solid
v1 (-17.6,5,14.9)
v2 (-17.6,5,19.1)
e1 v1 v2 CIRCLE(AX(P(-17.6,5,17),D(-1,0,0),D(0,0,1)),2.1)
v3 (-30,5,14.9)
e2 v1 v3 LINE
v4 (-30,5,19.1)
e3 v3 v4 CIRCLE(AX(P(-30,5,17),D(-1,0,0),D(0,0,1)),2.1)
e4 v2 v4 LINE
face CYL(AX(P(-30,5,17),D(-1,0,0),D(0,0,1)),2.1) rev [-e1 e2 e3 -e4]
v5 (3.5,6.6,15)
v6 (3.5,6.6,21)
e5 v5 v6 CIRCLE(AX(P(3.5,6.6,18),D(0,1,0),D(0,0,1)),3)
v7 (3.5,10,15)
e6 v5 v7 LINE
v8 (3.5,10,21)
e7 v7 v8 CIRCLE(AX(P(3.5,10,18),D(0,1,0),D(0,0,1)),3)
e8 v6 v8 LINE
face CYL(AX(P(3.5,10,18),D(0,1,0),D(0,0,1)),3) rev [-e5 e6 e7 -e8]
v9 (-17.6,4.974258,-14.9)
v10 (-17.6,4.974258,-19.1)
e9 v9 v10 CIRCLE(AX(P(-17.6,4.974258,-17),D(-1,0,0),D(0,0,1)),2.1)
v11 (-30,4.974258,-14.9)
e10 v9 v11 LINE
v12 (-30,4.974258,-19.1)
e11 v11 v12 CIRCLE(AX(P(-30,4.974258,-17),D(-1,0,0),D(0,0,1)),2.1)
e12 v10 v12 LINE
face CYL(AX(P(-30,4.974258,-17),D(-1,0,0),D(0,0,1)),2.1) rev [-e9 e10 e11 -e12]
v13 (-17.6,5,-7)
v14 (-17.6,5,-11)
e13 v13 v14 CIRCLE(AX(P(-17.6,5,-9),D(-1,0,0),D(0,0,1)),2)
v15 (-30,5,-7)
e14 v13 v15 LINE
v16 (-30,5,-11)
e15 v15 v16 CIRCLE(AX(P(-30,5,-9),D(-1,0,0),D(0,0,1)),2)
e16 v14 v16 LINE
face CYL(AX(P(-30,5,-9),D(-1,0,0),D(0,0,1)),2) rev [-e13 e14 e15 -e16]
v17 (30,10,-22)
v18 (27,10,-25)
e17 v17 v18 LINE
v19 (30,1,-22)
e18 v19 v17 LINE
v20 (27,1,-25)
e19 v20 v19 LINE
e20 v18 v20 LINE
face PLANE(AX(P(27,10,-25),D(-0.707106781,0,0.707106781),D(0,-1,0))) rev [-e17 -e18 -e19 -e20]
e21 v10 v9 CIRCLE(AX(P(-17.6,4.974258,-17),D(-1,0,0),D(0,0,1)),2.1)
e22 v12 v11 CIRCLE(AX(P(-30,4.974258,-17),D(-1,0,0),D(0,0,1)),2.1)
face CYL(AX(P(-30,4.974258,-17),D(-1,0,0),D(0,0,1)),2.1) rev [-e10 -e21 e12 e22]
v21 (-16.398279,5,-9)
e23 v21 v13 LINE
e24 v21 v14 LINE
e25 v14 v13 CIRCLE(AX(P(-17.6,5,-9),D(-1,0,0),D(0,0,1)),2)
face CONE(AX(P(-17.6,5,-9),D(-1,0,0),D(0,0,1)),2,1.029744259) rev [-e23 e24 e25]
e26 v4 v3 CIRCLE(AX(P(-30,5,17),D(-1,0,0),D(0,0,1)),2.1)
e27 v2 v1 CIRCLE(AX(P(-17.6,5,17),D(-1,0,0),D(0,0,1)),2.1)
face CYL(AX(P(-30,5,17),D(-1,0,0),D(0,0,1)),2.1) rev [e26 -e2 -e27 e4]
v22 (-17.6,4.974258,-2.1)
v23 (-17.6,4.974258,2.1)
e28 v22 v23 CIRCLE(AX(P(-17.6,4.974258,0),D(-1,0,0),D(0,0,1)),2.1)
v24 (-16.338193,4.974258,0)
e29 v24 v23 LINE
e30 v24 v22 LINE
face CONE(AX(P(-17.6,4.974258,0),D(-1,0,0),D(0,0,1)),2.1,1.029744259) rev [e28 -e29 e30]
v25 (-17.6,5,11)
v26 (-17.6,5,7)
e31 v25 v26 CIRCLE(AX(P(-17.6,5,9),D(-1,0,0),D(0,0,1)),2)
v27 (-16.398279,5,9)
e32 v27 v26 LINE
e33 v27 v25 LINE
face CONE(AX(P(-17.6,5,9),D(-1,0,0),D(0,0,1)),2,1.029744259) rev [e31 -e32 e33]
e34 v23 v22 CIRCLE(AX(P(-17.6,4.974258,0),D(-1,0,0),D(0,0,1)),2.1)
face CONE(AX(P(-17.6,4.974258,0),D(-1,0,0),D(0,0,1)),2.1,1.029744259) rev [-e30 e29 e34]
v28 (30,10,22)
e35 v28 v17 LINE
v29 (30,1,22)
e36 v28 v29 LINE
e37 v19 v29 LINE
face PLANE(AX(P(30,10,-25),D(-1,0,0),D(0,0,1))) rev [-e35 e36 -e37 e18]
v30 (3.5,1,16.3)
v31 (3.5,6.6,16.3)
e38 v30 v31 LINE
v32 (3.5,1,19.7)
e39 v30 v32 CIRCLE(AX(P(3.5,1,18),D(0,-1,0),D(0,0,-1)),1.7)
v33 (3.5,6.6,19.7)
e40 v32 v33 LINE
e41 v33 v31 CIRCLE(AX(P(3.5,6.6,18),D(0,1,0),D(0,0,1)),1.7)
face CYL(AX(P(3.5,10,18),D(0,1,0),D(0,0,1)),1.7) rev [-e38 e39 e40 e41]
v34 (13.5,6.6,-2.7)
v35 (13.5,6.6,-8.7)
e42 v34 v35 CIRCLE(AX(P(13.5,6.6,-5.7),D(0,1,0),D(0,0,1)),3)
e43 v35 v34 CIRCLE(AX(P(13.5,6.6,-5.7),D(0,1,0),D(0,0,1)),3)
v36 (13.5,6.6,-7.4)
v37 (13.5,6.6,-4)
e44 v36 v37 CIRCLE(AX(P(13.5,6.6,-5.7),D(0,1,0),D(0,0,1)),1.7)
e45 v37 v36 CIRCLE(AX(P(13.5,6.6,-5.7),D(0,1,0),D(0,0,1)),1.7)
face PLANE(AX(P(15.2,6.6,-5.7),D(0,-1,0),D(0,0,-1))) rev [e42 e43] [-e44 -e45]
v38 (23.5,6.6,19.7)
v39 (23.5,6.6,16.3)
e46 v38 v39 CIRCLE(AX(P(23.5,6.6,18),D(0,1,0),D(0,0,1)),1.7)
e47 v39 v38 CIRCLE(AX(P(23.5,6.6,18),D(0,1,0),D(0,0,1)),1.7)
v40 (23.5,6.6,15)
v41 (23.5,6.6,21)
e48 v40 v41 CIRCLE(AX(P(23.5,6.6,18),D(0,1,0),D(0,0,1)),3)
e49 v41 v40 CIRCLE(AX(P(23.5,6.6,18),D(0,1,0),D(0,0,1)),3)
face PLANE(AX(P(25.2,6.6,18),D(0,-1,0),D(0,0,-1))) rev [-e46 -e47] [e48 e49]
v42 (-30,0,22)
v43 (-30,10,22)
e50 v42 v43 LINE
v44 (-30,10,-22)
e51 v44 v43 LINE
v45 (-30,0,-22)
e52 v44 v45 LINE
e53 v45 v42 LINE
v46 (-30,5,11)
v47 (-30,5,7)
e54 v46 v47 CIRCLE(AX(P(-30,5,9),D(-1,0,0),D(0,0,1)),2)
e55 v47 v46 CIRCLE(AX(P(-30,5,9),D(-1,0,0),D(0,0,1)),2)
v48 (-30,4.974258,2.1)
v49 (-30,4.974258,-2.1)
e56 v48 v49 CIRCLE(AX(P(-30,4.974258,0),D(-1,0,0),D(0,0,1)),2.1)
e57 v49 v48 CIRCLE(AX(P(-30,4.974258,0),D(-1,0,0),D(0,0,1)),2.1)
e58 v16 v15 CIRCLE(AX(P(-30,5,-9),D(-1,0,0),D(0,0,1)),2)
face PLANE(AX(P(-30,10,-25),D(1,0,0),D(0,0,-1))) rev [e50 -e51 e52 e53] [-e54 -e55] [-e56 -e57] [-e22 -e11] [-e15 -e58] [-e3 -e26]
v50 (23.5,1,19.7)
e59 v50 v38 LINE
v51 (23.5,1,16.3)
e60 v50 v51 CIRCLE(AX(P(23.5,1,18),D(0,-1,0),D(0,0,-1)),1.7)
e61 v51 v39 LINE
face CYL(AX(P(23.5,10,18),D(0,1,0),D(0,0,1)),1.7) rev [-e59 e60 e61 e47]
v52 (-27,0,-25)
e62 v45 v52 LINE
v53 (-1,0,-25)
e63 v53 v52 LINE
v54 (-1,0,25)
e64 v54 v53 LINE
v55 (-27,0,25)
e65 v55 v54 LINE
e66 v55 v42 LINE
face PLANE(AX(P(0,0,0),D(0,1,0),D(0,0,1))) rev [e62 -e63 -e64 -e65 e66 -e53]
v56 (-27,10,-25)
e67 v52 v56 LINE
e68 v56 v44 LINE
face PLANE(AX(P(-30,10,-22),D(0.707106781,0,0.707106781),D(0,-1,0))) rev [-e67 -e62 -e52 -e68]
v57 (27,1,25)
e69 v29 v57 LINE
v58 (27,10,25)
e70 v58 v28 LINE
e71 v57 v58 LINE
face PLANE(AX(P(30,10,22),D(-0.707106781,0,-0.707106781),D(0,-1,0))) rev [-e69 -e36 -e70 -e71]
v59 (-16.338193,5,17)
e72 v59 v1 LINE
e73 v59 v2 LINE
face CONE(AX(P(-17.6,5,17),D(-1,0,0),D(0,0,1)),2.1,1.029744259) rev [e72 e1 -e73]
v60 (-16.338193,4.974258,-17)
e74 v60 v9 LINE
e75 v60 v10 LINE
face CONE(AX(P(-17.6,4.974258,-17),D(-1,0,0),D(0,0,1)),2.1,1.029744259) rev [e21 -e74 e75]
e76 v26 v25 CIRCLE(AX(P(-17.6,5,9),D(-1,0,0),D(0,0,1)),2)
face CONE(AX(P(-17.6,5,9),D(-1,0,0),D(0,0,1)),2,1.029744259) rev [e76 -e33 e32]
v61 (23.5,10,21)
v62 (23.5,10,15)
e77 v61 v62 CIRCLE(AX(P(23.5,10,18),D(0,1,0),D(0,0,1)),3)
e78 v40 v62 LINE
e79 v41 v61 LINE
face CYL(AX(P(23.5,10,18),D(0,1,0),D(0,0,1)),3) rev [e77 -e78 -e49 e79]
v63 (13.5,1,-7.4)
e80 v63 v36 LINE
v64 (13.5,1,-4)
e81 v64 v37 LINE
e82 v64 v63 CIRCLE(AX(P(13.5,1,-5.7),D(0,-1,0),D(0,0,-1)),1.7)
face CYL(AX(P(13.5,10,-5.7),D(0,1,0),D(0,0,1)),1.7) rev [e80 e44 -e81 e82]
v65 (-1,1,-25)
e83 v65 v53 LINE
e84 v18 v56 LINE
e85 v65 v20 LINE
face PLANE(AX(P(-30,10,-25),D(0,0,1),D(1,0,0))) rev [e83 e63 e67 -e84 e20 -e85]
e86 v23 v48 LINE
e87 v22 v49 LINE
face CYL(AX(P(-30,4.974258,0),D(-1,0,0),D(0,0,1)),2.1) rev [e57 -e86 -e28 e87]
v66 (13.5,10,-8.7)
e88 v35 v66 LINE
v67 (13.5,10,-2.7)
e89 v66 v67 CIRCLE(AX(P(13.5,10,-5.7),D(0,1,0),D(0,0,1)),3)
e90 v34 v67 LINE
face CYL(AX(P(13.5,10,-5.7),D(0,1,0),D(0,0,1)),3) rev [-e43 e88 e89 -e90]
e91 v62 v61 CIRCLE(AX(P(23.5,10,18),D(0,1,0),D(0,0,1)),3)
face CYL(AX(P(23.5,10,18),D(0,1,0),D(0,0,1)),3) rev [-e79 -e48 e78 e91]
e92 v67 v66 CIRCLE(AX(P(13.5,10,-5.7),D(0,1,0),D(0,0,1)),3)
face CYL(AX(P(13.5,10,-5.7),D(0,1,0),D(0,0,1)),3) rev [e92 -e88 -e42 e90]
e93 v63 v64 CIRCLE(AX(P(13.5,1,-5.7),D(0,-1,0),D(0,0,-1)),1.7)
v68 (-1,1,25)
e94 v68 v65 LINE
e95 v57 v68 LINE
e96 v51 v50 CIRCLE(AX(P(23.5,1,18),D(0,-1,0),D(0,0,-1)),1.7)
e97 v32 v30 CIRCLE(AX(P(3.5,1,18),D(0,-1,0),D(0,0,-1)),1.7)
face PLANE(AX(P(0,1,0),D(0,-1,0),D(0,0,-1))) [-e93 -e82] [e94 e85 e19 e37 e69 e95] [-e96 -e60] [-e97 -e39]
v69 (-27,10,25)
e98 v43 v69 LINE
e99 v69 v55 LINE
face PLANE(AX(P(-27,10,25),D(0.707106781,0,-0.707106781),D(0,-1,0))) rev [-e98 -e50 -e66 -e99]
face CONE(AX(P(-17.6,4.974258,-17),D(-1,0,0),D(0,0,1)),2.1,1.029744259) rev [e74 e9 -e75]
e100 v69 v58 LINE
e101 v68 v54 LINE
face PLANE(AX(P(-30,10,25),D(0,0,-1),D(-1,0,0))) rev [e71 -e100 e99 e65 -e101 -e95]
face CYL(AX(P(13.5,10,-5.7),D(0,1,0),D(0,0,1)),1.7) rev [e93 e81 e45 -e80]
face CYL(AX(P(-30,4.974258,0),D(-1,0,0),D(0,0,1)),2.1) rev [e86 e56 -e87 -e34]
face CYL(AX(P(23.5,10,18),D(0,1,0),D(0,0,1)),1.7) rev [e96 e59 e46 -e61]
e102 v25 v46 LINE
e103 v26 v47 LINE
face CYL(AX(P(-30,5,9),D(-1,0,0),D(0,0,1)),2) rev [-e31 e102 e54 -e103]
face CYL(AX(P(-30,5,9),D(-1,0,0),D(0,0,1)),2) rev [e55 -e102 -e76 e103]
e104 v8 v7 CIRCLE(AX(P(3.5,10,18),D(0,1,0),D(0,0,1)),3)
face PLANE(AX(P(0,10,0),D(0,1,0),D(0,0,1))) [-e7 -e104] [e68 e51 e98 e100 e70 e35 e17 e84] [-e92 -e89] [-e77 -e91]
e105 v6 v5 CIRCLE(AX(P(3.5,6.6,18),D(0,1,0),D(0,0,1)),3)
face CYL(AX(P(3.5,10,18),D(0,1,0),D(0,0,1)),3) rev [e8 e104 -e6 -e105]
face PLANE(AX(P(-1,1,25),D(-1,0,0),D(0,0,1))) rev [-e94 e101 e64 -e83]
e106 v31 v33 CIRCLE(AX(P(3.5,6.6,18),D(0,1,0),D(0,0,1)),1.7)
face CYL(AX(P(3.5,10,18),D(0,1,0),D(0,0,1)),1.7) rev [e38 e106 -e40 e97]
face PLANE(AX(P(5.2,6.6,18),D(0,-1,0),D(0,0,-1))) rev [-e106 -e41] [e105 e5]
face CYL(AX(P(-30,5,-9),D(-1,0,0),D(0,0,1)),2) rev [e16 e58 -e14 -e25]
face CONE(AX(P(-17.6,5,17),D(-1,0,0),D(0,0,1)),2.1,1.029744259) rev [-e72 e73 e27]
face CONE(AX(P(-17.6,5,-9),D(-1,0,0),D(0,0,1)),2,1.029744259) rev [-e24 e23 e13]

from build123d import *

# Parameters (mm, degrees)
SKETCH_1_W                = 60
SKETCH_1_H                = 50
EXTRUDE_1_DEPTH           = 10
SKETCH_5_W                = 31
SKETCH_5_H                = 50
CUT_EXTRUDE_1_DEPTH       = 1
CHAMFER_2_SIZE            = 3
HOLE_WIZARD_M5_1_D        = 4.2
HOLE_WIZARD_M5_1_DEPTH    = 12.4
HOLE_WIZARD_M5_1_TIP      = 1.2618073
HOLE_WIZARD_3_D           = 3.4
HOLE_WIZARD_3_DEPTH       = 12.4
HOLE_WIZARD_3_CBORE_D     = 6
HOLE_WIZARD_3_CBORE_DEPTH = 3.4
HOLE_WIZARD_3_TIP         = 1.021463052
MM_3_D                    = 4
MM_3_DEPTH                = 12.4
MM_3_TIP                  = 1.201721238


with BuildPart() as part:
    # 草图1 → 凸台-拉伸1 (new body)
    with BuildSketch(Plane(origin=(0, 0, 0), x_dir=(1, 0, 0), z_dir=(0, 1, 0))):
        Rectangle(SKETCH_1_W, SKETCH_1_H)
    extrude(amount=EXTRUDE_1_DEPTH)

    # 草图5 → 切除-拉伸1 (cut)
    with BuildSketch(Plane.XZ):
        with Locations((14.5, 0)):
            Rectangle(SKETCH_5_W, SKETCH_5_H)
    extrude(amount=-CUT_EXTRUDE_1_DEPTH, mode=Mode.SUBTRACT)

    # 倒角2
    chamfer_2_edges = [part.edges().sort_by_distance(p)[0] for p in [
        (30, 5.5, 25),
        (-30, 5, 25),
        (-30, 5, -25),
        (30, 5.5, -25),
    ]]
    chamfer(chamfer_2_edges, length=CHAMFER_2_SIZE)

    # M5 螺纹孔1
    with Locations(Plane.ZY.offset(30)):
        with Locations((17, 5), (-17, 4.974257895), (0, 4.974257895)):
            Hole(HOLE_WIZARD_M5_1_D / 2, depth=HOLE_WIZARD_M5_1_DEPTH)
            with Locations((0, 0, -(HOLE_WIZARD_M5_1_DEPTH + HOLE_WIZARD_M5_1_TIP / 2))):  # 118° drill point
                Cone(0, HOLE_WIZARD_M5_1_D / 2, HOLE_WIZARD_M5_1_TIP, mode=Mode.SUBTRACT)

    # 打孔尺寸(%根据)内六角圆柱头螺钉的类型3
    with Locations(Plane(origin=(0, 10, 0), x_dir=(1, 0, 0), z_dir=(0, 1, 0))):
        with Locations((23.5, -18), (3.5, -18), (13.5, 5.7)):
            CounterBoreHole(HOLE_WIZARD_3_D / 2, HOLE_WIZARD_3_CBORE_D / 2, HOLE_WIZARD_3_CBORE_DEPTH, depth=HOLE_WIZARD_3_DEPTH)
            with Locations((0, 0, -(HOLE_WIZARD_3_DEPTH + HOLE_WIZARD_3_TIP / 2))):  # 118° drill point
                Cone(0, HOLE_WIZARD_3_D / 2, HOLE_WIZARD_3_TIP, mode=Mode.SUBTRACT)

    # 大小mm 暗销孔3
    with Locations(Plane.ZY.offset(30)):
        with Locations((9, 5), (-9, 5)):
            Hole(MM_3_D / 2, depth=MM_3_DEPTH)
            with Locations((0, 0, -(MM_3_DEPTH + MM_3_TIP / 2))):  # 118° drill point
                Cone(0, MM_3_D / 2, MM_3_TIP, mode=Mode.SUBTRACT)


solid = part.part
